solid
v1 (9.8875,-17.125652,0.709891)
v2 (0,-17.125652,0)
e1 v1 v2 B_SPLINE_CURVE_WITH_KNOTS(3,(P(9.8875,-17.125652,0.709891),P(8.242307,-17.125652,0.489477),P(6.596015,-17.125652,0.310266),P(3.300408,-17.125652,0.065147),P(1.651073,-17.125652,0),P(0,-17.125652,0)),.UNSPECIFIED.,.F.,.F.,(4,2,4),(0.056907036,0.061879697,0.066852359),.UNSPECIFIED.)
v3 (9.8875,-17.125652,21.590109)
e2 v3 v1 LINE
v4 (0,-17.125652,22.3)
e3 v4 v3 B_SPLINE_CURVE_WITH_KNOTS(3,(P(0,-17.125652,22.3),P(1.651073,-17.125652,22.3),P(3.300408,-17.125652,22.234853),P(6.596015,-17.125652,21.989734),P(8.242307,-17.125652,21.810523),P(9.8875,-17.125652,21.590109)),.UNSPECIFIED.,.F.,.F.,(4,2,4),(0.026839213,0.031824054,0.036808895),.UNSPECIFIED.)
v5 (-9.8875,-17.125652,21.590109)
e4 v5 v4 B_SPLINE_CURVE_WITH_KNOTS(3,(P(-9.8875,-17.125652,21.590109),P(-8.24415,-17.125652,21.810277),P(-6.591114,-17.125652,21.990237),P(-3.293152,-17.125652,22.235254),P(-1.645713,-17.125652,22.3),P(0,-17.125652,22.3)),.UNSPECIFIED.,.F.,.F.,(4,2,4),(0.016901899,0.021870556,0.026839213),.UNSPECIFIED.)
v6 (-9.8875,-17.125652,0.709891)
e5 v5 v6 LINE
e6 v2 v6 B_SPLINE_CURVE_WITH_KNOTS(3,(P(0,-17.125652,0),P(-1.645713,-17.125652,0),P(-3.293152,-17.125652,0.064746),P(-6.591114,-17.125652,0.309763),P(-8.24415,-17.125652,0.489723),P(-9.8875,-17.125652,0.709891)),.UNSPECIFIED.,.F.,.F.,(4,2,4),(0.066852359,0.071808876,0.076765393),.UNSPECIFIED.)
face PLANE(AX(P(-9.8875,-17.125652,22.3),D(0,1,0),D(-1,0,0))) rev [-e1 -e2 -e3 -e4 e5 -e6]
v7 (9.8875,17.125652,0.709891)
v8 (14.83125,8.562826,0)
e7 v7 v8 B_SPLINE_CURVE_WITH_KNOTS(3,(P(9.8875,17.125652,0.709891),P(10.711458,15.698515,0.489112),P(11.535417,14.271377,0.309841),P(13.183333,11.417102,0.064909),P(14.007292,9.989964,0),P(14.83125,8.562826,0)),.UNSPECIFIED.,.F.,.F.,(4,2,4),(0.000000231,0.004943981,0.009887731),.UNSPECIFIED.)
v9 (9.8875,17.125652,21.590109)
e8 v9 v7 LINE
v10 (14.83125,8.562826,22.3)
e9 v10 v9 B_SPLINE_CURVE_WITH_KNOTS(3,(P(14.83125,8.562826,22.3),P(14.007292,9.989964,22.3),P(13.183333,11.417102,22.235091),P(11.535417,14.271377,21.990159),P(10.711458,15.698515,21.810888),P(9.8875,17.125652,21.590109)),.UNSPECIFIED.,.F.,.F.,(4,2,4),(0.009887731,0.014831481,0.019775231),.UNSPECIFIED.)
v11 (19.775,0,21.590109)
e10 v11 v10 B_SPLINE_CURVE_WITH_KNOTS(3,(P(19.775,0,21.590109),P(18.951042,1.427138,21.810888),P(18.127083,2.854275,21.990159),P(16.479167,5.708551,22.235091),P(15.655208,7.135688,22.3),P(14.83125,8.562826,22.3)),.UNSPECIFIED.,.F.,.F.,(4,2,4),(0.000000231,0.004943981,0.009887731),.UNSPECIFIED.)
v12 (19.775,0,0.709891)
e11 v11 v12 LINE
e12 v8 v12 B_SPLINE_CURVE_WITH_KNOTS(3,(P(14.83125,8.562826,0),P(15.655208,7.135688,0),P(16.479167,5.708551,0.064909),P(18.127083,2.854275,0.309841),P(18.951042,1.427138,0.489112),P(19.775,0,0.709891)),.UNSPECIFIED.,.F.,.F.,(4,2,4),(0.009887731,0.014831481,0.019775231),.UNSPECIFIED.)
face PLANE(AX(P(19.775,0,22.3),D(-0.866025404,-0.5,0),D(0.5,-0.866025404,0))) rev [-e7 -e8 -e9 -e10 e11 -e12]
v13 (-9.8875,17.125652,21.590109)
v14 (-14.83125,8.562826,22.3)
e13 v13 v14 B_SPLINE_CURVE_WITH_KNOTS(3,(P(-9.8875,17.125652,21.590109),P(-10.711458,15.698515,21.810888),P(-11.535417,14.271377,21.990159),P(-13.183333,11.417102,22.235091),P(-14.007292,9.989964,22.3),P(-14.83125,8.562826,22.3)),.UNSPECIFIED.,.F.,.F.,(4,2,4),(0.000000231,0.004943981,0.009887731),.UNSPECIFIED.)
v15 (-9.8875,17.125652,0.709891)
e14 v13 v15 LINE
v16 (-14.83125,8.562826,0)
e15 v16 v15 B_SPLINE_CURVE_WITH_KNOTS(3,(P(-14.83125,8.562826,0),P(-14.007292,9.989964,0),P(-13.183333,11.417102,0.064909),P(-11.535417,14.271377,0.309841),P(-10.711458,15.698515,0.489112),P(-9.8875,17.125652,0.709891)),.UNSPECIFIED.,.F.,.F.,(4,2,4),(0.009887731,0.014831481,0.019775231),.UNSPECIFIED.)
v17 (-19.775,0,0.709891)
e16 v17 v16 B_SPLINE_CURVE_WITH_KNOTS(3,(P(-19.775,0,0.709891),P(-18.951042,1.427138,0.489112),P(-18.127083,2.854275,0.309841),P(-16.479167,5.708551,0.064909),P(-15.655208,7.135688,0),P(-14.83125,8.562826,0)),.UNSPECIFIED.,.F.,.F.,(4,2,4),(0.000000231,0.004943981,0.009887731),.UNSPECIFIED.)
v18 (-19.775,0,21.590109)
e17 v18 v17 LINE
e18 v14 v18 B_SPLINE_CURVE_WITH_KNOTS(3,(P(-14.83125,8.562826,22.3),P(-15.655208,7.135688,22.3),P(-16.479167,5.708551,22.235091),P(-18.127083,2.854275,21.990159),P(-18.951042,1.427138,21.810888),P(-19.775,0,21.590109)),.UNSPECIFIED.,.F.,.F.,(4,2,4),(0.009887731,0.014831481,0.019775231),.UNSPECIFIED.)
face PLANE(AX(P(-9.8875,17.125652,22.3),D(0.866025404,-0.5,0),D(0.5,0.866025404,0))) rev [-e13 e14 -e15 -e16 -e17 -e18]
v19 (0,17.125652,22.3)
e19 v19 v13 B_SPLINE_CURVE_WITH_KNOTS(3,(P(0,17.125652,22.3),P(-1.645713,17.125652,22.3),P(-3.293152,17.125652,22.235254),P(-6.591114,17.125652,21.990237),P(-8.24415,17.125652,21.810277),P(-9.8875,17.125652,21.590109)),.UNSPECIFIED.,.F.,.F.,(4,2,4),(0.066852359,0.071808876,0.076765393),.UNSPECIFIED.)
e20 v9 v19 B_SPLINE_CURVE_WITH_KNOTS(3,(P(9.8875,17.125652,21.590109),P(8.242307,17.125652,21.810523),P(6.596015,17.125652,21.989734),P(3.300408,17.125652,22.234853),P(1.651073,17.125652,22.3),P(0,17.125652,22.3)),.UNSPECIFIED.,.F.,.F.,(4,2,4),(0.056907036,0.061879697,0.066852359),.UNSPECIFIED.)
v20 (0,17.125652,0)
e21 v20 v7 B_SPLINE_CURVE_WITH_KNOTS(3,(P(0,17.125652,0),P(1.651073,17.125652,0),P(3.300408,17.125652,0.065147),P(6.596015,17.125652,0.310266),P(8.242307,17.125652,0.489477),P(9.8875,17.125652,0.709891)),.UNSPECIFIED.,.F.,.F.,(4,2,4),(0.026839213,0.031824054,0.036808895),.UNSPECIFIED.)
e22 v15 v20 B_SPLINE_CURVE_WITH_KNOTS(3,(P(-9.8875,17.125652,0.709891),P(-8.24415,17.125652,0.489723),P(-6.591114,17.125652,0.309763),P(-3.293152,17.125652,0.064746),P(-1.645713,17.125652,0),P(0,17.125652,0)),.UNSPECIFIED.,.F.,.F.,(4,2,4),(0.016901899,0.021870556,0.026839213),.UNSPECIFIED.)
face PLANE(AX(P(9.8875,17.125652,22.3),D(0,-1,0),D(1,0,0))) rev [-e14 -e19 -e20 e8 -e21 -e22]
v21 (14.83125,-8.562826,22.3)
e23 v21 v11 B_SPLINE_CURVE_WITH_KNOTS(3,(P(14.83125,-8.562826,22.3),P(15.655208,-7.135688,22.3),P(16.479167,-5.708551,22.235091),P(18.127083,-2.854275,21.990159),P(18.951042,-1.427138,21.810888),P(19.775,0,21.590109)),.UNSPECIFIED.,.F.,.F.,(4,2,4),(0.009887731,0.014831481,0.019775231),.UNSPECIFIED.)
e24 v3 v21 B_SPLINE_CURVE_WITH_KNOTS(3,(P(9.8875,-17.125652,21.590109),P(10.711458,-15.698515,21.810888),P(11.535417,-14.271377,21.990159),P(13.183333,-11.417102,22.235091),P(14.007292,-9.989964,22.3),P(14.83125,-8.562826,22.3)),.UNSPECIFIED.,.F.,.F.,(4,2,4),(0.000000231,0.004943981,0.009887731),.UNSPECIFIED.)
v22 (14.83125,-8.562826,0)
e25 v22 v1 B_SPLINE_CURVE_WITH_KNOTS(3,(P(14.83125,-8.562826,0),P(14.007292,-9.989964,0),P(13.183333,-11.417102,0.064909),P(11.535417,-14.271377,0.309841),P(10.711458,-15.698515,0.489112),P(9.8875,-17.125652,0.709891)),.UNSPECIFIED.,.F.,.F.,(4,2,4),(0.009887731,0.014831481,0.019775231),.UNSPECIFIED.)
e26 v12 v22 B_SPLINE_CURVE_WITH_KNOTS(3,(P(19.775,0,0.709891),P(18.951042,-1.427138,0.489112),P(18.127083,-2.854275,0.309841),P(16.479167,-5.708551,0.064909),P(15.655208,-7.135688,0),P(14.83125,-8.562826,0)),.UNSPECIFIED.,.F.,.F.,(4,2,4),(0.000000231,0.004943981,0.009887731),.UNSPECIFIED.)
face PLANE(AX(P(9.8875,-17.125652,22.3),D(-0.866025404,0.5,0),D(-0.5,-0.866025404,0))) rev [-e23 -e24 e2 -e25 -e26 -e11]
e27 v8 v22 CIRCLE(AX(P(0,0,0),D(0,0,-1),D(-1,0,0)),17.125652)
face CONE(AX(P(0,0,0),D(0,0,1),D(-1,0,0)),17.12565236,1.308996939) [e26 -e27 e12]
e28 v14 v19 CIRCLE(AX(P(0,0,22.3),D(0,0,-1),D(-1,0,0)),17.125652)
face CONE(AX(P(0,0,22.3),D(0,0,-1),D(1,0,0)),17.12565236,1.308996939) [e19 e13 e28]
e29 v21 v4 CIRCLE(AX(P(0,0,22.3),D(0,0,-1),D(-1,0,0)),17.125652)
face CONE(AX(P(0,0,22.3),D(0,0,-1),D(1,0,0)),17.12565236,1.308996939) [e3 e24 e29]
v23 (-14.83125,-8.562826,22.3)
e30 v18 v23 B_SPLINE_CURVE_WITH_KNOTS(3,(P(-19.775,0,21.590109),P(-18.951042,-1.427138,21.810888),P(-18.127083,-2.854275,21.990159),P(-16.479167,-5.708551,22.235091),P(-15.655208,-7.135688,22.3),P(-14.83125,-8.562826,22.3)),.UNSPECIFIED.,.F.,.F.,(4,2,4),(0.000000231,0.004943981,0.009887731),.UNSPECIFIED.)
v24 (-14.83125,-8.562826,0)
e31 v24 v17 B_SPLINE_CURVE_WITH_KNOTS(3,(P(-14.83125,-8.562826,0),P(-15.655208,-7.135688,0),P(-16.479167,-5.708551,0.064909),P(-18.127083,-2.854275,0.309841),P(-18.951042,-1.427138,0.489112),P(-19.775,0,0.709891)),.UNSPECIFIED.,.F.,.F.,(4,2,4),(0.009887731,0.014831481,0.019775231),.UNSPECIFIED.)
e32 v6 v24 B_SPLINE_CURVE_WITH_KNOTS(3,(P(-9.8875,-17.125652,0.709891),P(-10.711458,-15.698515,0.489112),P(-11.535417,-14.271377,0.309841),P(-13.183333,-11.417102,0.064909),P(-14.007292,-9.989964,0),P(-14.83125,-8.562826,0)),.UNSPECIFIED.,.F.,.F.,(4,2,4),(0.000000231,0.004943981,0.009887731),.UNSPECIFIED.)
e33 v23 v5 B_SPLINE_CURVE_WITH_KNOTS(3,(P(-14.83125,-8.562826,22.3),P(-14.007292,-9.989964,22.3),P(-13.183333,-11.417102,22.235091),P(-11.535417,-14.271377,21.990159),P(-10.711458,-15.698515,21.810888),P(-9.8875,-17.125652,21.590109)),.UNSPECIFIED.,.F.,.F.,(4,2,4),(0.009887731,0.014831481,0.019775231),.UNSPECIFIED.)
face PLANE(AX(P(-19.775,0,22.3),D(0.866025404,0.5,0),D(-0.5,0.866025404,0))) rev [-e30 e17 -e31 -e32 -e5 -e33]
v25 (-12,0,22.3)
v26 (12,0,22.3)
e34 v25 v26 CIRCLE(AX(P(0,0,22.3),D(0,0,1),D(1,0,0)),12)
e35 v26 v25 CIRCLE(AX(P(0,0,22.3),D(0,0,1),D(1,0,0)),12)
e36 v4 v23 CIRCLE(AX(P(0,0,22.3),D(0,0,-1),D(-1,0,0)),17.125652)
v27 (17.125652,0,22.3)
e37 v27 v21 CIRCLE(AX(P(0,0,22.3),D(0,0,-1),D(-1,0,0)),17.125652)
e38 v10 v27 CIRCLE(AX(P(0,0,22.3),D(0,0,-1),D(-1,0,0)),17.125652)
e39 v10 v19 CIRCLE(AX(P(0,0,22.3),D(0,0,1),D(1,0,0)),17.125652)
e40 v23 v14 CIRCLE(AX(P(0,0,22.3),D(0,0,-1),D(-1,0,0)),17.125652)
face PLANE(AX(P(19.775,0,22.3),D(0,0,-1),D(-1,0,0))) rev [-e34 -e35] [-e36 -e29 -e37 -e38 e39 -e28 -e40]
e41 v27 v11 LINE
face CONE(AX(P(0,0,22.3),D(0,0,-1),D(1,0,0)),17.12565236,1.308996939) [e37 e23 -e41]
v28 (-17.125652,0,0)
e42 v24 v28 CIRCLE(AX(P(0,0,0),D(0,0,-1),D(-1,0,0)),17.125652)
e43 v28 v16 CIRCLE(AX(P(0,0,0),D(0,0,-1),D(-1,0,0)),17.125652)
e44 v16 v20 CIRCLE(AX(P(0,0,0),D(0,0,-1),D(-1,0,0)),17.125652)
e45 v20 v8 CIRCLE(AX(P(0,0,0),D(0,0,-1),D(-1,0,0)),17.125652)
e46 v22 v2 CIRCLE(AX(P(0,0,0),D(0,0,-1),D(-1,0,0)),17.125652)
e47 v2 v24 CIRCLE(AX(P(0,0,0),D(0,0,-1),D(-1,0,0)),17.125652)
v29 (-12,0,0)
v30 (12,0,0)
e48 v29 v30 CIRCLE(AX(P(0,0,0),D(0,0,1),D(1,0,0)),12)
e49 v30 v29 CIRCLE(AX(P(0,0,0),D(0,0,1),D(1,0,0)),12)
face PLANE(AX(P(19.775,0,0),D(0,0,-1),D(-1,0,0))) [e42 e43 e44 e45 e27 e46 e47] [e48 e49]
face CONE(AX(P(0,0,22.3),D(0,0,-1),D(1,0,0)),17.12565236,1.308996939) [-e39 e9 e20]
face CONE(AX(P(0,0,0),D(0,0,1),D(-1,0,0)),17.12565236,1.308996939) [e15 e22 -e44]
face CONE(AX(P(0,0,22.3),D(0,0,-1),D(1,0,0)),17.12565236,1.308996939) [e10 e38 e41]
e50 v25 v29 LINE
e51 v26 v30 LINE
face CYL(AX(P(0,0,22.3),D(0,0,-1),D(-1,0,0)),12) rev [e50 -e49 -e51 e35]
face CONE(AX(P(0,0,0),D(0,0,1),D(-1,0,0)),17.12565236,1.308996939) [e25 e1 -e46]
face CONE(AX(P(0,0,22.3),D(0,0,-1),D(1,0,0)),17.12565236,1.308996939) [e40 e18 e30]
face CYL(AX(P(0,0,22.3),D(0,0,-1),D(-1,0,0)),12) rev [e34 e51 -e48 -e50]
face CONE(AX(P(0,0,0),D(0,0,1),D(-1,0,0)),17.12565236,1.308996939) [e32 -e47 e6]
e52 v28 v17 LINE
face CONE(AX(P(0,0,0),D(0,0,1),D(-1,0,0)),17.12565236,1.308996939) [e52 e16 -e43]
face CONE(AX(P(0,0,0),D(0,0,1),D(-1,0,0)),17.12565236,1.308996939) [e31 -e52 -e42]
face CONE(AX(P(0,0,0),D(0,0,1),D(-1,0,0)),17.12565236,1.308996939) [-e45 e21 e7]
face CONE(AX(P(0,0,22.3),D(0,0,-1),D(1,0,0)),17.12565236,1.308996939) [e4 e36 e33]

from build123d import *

# Parameters (mm, degrees)
SKETCH1_R          = 12
BASE_EXTRUDE_DEPTH = 22.3
SKETCH2_OUTSIDE_W  = 336.56
SKETCH2_OUTSIDE_H  = 331.262
SKETCH2_OUTSIDE_R  = 17.12565236
CUT_EXTRUDE1_DEPTH = 38
CUT_EXTRUDE1_DRAFT = -75
SKETCH3_OUTSIDE_W  = 336.56
SKETCH3_OUTSIDE_H  = 331.262
SKETCH3_OUTSIDE_R  = 17.12565236
CUT_EXTRUDE2_DEPTH = 38
CUT_EXTRUDE2_DRAFT = -75


with BuildPart() as part:
    # Sketch1 → Base-Extrude (new body)
    with BuildSketch(Plane.XY):
        Polygon((9.8875, 17.12565236), (-9.8875, 17.12565236), (-19.775, 0), (-9.8875, -17.12565236), (9.8875, -17.12565236), (19.775, 0), align=None)
        Circle(SKETCH1_R, mode=Mode.SUBTRACT)
    extrude(amount=BASE_EXTRUDE_DEPTH)


with BuildPart() as cut_extrude1_tool:
    # Sketch2 outside → Cut-Extrude1 (with draft: the straight prism first)
    with BuildSketch(Plane(origin=(0, 0, 0), x_dir=(-1, 0, 0), z_dir=(0, 0, -1))):
        Rectangle(SKETCH2_OUTSIDE_W, SKETCH2_OUTSIDE_H)
        Circle(SKETCH2_OUTSIDE_R, mode=Mode.SUBTRACT)
    extrude(amount=-CUT_EXTRUDE1_DEPTH)
    # Cut-Extrude1: the draft: its side faces are tilted about the plane it starts from
    cut_extrude1_sides = [cut_extrude1_tool.faces().sort_by_distance(p)[0] for p in [
        (0, -165.631, 19),
        (-168.28, 0, 19),
        (0, 165.631, 19),
        (168.28, 0, 19),
        (17.12565236, 0, 19),
    ]]
    draft(cut_extrude1_sides, Plane(origin=(0, 0, 0), x_dir=(-1, 0, 0), z_dir=(0, 0, -1)), CUT_EXTRUDE1_DRAFT)


with BuildPart() as part_1:
    add(part.part)

    # Cut-Extrude1: cut by cut_extrude1_tool
    add(cut_extrude1_tool.part, mode=Mode.SUBTRACT)


with BuildPart() as cut_extrude2_tool:
    # Sketch3 outside → Cut-Extrude2 (with draft: the straight prism first)
    with BuildSketch(Plane.XY.offset(22.3)):
        Rectangle(SKETCH3_OUTSIDE_W, SKETCH3_OUTSIDE_H)
        Circle(SKETCH3_OUTSIDE_R, mode=Mode.SUBTRACT)
    extrude(amount=-CUT_EXTRUDE2_DEPTH)
    # Cut-Extrude2: the draft: its side faces are tilted about the plane it starts from
    cut_extrude2_sides = [cut_extrude2_tool.faces().sort_by_distance(p)[0] for p in [
        (0, -165.631, 3.3),
        (168.28, 0, 3.3),
        (0, 165.631, 3.3),
        (-168.28, 0, 3.3),
        (-17.12565236, 0, 3.3),
    ]]
    draft(cut_extrude2_sides, Plane.XY.offset(22.3), CUT_EXTRUDE2_DRAFT)


with BuildPart() as part_2:
    add(part_1.part)

    # Cut-Extrude2: cut by cut_extrude2_tool
    add(cut_extrude2_tool.part, mode=Mode.SUBTRACT)


solid = part_2.part
